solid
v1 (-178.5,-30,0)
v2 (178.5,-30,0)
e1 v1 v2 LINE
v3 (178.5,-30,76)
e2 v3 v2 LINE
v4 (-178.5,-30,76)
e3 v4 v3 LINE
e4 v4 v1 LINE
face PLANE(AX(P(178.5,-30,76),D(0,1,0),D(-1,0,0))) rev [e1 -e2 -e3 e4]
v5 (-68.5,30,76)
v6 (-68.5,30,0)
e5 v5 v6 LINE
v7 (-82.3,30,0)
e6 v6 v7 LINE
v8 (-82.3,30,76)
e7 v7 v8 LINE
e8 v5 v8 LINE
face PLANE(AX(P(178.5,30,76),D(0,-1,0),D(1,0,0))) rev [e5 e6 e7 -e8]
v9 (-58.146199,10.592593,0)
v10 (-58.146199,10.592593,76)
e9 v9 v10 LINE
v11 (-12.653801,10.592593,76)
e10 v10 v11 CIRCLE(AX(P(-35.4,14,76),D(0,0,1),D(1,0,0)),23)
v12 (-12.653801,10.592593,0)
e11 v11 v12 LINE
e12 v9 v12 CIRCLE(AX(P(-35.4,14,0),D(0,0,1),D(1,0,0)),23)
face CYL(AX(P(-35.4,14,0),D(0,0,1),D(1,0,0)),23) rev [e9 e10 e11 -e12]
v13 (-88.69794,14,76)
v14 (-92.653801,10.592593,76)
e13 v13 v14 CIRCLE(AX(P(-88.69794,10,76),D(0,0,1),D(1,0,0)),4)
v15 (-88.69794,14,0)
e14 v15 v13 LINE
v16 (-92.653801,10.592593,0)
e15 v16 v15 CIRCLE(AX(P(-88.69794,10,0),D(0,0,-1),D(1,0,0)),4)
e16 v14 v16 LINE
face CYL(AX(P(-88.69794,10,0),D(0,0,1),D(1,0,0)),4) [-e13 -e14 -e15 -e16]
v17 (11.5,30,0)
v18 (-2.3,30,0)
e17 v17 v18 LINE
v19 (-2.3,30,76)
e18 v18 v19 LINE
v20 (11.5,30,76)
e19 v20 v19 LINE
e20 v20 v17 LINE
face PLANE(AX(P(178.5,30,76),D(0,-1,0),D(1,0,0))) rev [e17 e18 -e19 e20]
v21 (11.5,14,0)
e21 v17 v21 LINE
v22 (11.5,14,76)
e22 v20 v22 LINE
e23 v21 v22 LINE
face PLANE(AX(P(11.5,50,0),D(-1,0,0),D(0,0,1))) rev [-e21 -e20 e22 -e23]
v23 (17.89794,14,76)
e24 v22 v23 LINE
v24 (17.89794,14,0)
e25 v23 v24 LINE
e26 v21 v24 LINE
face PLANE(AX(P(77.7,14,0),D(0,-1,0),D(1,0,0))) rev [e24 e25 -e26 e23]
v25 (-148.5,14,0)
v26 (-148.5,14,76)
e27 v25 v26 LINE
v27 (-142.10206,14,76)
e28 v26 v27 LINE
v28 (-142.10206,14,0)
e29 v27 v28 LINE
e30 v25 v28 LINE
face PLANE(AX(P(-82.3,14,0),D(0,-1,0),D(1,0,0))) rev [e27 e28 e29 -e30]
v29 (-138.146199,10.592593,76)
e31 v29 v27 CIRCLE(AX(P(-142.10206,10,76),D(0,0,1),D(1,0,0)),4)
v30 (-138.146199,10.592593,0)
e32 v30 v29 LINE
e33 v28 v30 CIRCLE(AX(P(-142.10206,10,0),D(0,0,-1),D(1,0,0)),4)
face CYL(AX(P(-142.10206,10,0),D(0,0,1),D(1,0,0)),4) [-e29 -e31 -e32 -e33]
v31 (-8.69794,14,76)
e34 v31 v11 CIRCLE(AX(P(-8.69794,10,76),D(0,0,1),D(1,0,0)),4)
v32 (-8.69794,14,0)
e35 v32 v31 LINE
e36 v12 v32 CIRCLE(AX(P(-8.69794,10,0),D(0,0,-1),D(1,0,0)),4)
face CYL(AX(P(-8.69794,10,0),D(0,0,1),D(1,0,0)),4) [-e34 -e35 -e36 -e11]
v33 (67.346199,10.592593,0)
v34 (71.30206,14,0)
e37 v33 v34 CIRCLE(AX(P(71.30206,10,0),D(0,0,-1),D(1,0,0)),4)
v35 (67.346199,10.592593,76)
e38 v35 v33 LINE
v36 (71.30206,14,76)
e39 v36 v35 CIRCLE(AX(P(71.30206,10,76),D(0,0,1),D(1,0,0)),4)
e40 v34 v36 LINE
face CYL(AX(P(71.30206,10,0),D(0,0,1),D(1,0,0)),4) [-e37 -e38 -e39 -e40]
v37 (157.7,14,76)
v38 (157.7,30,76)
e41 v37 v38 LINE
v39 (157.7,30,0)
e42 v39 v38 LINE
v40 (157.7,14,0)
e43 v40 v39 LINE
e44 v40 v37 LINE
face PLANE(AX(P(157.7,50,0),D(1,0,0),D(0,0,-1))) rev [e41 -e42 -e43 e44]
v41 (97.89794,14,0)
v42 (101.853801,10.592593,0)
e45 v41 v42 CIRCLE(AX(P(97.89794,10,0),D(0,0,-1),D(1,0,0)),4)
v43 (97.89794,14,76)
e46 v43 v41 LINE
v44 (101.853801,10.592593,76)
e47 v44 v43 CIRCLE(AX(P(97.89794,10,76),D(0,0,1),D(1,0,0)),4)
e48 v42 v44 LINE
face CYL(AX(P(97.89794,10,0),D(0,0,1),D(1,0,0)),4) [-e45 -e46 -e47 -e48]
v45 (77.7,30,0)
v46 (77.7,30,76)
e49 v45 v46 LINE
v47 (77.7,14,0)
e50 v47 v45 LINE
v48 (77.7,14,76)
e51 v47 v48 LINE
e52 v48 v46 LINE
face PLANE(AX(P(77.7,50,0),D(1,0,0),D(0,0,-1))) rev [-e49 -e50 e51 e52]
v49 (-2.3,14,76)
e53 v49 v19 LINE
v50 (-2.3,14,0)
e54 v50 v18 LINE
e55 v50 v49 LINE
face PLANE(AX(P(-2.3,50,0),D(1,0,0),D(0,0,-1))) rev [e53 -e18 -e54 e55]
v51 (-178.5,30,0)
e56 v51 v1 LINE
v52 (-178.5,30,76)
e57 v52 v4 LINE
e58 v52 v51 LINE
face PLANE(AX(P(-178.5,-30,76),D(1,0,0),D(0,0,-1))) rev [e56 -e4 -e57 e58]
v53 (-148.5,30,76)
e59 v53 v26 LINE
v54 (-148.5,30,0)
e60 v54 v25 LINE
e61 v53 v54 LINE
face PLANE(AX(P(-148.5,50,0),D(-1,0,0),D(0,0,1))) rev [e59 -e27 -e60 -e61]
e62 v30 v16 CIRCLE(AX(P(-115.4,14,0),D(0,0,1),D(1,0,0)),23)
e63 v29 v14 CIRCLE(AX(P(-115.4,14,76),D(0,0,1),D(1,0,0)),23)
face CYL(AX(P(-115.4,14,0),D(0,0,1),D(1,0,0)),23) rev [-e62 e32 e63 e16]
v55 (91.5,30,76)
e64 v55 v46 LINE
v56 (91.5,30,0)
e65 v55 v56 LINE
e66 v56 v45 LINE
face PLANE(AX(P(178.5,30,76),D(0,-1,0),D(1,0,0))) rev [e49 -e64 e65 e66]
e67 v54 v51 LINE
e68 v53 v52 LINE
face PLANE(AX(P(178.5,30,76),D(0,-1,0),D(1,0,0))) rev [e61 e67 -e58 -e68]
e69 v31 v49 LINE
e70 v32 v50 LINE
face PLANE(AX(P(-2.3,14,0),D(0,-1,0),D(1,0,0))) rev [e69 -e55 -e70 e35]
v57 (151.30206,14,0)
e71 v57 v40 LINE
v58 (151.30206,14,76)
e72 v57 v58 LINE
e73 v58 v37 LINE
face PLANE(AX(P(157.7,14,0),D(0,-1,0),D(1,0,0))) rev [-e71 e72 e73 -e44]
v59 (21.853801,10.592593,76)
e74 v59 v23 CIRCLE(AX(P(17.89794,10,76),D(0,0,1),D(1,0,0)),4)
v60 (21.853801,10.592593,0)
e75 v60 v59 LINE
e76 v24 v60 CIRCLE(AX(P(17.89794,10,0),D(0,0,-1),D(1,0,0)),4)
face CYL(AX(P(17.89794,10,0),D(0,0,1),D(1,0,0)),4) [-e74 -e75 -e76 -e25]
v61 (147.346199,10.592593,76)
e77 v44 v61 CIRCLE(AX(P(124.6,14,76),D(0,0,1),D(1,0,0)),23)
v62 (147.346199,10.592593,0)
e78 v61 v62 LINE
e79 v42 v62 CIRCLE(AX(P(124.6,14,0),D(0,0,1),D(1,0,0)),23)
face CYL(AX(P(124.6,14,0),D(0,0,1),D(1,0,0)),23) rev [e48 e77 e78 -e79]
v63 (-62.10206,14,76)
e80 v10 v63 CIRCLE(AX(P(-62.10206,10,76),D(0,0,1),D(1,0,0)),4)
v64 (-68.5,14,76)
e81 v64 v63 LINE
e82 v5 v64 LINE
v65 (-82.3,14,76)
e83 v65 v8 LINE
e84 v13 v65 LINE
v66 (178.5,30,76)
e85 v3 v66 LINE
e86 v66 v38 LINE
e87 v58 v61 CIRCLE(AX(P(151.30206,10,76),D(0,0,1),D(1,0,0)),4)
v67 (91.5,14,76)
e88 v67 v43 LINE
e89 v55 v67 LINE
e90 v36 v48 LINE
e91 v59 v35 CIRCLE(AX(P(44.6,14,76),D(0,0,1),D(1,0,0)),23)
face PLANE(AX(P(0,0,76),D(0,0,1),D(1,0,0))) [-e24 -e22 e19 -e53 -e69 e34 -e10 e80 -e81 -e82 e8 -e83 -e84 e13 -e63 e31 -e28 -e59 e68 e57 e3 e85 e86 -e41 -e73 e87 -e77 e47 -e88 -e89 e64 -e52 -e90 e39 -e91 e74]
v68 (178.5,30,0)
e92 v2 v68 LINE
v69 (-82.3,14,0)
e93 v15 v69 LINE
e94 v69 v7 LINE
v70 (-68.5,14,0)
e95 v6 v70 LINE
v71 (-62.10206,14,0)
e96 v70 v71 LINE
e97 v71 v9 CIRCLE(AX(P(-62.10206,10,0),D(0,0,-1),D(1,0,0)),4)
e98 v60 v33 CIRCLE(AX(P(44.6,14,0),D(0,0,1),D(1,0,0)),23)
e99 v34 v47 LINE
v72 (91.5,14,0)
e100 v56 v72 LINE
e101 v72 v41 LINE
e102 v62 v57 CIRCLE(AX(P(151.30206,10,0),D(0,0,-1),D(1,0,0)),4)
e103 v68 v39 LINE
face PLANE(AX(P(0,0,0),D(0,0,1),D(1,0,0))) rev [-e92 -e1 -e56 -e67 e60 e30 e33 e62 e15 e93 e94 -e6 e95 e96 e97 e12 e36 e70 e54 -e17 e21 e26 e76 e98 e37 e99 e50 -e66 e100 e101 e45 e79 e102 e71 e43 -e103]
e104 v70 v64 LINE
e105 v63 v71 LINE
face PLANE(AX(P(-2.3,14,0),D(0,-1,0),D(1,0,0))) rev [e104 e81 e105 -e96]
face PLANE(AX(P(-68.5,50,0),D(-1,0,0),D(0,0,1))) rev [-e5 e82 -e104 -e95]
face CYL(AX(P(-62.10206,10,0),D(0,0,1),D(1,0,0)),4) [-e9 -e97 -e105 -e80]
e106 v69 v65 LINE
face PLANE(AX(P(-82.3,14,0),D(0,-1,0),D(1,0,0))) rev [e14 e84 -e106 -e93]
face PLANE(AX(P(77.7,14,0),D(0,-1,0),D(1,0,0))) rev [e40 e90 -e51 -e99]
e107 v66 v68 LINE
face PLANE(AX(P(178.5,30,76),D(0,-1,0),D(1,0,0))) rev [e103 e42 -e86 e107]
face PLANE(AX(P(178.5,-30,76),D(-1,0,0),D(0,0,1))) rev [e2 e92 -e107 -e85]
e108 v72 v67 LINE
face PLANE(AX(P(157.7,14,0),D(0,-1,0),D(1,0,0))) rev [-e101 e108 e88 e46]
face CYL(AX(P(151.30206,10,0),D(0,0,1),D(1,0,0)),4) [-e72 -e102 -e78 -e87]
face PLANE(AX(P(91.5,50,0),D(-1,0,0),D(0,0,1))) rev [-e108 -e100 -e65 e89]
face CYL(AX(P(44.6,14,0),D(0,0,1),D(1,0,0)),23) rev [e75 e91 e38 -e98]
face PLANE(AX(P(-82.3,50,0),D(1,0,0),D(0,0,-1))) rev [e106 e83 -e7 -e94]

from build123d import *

# Parameters (mm, degrees)
SKETCH1_W              = 357
SKETCH1_H              = 60
BOSS_EXTRUDE1_DEPTH    = 76
SKETCH2_W              = 66.2
SKETCH2_H              = 36
CUT_EXTRUDE1_DEPTH     = 197.311614532
SKETCH3_R              = 23
CUT_EXTRUDE2_DEPTH     = 197.311614532
FILLET1_R              = 4
LPATTERN1_COUNT        = 4
LPATTERN1_PITCH        = 80
FILLET1_OF_LPATTERN1_R = 4


with BuildPart() as part:
    # Sketch1 → Boss-Extrude1 (new body)
    with BuildSketch(Plane.XY):
        Rectangle(SKETCH1_W, SKETCH1_H)
    extrude(amount=BOSS_EXTRUDE1_DEPTH)

    # Sketch2 → Cut-Extrude1 (cut, through all)
    with BuildSketch(Plane.XY.offset(76)):
        with Locations((-115.4, 32)):
            Rectangle(SKETCH2_W, SKETCH2_H)
    cut_extrude1 = extrude(amount=-CUT_EXTRUDE1_DEPTH, mode=Mode.SUBTRACT)

    # Sketch3 → Cut-Extrude2 (cut, through all)
    with BuildSketch(Plane.XY.offset(76)):
        with Locations((-115.4, 14)):
            Circle(SKETCH3_R)
    cut_extrude2 = extrude(amount=-CUT_EXTRUDE2_DEPTH, mode=Mode.SUBTRACT)

    # Fillet1
    fillet1_edges = [part.edges().sort_by_distance(p)[0] for p in [
        (-138.4, 14, 38),
        (-92.4, 14, 38),
    ]]
    fillet(fillet1_edges, radius=FILLET1_R)

    # LPattern1: Cut-Extrude1, Cut-Extrude2 ×4
    with Locations(*[(i * LPATTERN1_PITCH, 0, 0) for i in range(1, LPATTERN1_COUNT)]):
        add(cut_extrude1, mode=Mode.SUBTRACT)
        add(cut_extrude2, mode=Mode.SUBTRACT)

    # Fillet1 of LPattern1
    fillet1_of_lpattern1_edges = [part.edges().sort_by_distance(p)[0] for p in [
        (-58.4, 14, 38),
        (-12.4, 14, 38),
        (21.6, 14, 38),
        (67.6, 14, 38),
        (101.6, 14, 38),
        (147.6, 14, 38),
    ]]
    fillet(fillet1_of_lpattern1_edges, radius=FILLET1_OF_LPATTERN1_R)


solid = part.part
